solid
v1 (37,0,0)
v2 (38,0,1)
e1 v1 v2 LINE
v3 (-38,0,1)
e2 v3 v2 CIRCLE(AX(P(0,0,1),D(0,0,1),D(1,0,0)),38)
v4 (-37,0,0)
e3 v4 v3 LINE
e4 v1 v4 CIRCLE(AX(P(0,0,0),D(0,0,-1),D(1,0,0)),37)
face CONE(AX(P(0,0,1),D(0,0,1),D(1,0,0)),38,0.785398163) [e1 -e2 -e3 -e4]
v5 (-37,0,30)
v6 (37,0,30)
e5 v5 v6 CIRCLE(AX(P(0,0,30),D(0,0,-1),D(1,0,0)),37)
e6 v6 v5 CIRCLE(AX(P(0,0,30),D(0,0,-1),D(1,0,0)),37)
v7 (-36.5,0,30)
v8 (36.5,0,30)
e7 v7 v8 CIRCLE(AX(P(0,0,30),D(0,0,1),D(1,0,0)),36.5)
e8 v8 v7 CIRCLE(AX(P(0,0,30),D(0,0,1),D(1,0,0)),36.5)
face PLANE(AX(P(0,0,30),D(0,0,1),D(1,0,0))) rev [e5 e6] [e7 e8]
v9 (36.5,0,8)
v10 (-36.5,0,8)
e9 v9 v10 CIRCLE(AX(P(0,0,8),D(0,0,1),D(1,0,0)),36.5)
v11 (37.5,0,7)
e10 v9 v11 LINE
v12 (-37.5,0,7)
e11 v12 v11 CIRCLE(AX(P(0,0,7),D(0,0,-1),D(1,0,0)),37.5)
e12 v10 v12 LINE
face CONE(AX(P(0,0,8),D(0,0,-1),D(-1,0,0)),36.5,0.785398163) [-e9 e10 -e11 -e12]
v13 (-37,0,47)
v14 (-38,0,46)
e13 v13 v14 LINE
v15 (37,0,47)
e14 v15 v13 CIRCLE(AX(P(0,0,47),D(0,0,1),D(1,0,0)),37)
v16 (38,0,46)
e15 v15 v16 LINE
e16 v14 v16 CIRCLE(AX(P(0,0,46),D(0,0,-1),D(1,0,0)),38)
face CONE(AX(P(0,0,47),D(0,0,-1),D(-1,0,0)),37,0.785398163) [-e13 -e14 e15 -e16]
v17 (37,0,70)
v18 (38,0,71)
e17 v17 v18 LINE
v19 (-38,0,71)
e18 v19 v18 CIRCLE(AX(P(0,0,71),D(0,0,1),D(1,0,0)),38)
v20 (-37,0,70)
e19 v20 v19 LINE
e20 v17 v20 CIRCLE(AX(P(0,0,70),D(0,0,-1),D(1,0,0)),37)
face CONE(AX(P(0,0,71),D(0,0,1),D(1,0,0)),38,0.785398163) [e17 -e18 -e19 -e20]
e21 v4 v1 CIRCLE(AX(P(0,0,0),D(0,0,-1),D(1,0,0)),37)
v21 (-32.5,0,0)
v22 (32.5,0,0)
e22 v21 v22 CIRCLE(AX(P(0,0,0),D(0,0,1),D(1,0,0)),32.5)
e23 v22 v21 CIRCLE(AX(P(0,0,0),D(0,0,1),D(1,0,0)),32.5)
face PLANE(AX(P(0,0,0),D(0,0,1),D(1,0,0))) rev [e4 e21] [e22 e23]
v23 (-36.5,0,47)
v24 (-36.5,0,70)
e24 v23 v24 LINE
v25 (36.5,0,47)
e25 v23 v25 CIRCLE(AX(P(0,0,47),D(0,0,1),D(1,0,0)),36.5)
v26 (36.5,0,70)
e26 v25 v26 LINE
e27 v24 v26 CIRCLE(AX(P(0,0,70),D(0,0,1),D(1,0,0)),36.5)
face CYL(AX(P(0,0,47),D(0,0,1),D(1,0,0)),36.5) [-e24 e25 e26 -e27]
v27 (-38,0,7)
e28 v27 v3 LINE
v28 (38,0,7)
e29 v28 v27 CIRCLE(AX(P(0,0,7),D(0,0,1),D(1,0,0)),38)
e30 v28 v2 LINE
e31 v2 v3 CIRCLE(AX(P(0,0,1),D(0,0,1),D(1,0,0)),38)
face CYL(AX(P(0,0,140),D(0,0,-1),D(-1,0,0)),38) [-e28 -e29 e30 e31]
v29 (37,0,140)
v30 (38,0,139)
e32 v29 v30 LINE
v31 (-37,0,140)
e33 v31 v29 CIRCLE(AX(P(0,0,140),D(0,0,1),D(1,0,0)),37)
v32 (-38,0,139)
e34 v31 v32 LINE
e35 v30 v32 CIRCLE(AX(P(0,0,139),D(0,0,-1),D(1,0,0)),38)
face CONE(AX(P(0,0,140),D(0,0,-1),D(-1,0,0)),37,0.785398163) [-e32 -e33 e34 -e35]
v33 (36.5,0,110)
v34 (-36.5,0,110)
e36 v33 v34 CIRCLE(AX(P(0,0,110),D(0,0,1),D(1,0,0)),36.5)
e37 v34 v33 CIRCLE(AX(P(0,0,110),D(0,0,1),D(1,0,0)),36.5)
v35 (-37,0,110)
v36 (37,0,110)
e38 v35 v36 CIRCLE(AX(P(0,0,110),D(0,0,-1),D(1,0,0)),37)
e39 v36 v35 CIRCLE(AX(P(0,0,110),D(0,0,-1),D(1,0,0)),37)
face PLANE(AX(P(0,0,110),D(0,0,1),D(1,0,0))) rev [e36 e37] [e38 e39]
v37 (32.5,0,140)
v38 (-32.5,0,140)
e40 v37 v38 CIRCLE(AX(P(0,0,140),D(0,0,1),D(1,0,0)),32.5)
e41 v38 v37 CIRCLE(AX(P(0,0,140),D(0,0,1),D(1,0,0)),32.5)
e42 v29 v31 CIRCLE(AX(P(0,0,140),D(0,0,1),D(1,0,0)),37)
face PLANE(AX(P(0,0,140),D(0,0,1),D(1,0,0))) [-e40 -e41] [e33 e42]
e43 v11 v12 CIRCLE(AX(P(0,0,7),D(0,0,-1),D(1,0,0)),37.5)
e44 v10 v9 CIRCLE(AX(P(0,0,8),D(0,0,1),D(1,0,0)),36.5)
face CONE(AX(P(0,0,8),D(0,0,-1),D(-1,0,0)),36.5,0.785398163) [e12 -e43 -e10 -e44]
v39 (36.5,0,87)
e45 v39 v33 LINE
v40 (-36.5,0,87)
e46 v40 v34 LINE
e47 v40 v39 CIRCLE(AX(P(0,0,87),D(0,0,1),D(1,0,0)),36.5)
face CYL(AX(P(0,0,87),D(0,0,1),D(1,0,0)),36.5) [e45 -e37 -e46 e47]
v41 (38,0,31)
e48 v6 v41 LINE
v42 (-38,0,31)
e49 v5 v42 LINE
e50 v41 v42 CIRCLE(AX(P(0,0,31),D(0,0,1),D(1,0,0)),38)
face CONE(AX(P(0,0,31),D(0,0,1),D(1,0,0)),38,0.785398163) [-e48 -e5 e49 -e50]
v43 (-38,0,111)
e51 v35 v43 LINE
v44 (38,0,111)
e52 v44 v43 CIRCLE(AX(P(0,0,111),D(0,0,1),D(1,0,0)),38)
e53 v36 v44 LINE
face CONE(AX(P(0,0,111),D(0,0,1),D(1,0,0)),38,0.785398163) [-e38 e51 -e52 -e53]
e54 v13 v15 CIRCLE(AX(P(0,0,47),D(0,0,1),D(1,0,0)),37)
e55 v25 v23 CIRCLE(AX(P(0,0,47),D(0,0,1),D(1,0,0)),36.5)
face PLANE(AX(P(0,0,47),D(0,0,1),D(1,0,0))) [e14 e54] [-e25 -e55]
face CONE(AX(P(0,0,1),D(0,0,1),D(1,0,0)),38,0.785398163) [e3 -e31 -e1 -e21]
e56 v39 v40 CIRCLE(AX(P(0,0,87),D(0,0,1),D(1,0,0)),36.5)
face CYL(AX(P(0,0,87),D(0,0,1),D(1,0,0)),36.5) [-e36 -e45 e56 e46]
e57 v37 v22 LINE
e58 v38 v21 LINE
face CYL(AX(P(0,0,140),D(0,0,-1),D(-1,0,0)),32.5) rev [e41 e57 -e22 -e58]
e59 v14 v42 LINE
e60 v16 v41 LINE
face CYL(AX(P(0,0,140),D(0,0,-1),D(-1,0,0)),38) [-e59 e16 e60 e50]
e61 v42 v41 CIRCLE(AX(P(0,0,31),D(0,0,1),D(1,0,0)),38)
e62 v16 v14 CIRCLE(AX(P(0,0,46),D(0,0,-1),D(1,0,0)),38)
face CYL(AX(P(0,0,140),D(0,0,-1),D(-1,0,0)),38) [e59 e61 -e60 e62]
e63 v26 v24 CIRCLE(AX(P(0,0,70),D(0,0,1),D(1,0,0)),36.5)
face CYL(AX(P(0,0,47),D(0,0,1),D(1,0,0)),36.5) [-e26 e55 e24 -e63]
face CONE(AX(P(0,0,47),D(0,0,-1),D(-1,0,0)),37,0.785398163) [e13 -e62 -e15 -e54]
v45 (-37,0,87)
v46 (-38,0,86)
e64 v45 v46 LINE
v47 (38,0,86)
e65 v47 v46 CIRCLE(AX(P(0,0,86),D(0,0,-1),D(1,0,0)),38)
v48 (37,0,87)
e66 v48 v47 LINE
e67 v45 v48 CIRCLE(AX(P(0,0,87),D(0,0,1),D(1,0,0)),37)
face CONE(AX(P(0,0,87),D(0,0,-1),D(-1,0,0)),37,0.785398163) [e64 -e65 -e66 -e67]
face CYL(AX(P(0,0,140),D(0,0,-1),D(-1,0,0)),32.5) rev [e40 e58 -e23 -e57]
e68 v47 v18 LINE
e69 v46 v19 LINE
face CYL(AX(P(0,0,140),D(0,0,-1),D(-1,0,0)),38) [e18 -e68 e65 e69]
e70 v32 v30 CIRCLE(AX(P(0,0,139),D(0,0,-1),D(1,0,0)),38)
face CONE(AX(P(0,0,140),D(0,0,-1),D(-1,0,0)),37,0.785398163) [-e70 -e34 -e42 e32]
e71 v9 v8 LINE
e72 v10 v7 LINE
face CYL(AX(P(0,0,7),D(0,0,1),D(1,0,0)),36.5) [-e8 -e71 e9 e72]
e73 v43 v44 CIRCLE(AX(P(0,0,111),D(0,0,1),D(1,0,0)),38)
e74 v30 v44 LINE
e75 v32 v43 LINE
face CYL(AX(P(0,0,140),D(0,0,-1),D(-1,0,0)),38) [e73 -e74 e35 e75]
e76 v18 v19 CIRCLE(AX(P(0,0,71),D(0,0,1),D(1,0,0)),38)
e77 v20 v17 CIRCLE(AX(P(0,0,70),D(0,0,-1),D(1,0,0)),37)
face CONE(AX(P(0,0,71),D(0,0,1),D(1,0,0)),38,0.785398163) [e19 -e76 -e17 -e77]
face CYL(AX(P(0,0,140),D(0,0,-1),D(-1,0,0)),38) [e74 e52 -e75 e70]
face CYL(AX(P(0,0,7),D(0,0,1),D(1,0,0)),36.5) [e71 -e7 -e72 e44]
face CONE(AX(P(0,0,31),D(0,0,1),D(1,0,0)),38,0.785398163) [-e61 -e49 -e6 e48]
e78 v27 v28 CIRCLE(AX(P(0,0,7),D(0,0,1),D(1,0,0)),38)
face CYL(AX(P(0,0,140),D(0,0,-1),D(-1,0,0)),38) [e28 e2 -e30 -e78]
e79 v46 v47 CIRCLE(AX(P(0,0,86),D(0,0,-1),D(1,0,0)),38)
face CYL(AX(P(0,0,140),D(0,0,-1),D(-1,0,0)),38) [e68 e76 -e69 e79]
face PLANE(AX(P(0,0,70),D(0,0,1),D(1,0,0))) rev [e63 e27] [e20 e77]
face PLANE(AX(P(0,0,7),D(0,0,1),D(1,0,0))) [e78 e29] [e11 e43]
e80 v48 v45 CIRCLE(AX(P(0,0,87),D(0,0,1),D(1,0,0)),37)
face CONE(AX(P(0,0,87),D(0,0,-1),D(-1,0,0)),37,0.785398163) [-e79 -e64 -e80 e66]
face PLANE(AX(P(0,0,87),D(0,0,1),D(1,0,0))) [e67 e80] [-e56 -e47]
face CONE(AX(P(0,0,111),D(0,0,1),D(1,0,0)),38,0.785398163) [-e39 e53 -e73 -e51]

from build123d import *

# Parameters (mm, degrees)
SKETCH_1_R             = 38
SKETCH_1_R_2           = 32.5
EXTRUDE_1_DEPTH        = 140
CHAMFER_1_SIZE         = 1
CUT_EXTRUDE_START      = -23
SKETCH_2_R             = 38
SKETCH_2_R_2           = 36.5
CUT_EXTRUDE_1_DEPTH    = 23
PATTERN_LINEAR_1_COUNT = 3
PATTERN_LINEAR_1_PITCH = 40
CHAMFER_2_SIZE         = 1


with BuildPart() as part:
    # 草图1 → 凸台-拉伸1 (new body)
    with BuildSketch(Plane.XY):
        Circle(SKETCH_1_R)
        Circle(SKETCH_1_R_2, mode=Mode.SUBTRACT)
    extrude(amount=EXTRUDE_1_DEPTH)

    # 倒角1
    chamfer_1_edges = [part.edges().sort_by_distance(p)[0] for p in [
        (-38, 0, 140),
    ]]
    chamfer(chamfer_1_edges, length=CHAMFER_1_SIZE)

    # 草图2 → 切除-拉伸1 (cut)
    with BuildSketch(Plane.XY.offset(110).offset(CUT_EXTRUDE_START)):
        Circle(SKETCH_2_R)
        Circle(SKETCH_2_R_2, mode=Mode.SUBTRACT)
    cut_extrude_1 = extrude(amount=CUT_EXTRUDE_1_DEPTH, mode=Mode.SUBTRACT)

    # 阵列(线性)1: 切除-拉伸1 ×3
    with Locations(*[(0, 0, -i * PATTERN_LINEAR_1_PITCH) for i in range(1, PATTERN_LINEAR_1_COUNT)]):
        add(cut_extrude_1, mode=Mode.SUBTRACT)

    # 倒角2
    chamfer_2_edges = [part.edges().sort_by_distance(p)[0] for p in [
        (-38, 0, 87),
        (-38, 0, 110),
        (-38, 0, 0),
        (-38, 0, 47),
        (-38, 0, 70),
        (-36.5, 0, 7),
        (-38, 0, 30),
    ]]
    chamfer(chamfer_2_edges, length=CHAMFER_2_SIZE)


solid = part.part
